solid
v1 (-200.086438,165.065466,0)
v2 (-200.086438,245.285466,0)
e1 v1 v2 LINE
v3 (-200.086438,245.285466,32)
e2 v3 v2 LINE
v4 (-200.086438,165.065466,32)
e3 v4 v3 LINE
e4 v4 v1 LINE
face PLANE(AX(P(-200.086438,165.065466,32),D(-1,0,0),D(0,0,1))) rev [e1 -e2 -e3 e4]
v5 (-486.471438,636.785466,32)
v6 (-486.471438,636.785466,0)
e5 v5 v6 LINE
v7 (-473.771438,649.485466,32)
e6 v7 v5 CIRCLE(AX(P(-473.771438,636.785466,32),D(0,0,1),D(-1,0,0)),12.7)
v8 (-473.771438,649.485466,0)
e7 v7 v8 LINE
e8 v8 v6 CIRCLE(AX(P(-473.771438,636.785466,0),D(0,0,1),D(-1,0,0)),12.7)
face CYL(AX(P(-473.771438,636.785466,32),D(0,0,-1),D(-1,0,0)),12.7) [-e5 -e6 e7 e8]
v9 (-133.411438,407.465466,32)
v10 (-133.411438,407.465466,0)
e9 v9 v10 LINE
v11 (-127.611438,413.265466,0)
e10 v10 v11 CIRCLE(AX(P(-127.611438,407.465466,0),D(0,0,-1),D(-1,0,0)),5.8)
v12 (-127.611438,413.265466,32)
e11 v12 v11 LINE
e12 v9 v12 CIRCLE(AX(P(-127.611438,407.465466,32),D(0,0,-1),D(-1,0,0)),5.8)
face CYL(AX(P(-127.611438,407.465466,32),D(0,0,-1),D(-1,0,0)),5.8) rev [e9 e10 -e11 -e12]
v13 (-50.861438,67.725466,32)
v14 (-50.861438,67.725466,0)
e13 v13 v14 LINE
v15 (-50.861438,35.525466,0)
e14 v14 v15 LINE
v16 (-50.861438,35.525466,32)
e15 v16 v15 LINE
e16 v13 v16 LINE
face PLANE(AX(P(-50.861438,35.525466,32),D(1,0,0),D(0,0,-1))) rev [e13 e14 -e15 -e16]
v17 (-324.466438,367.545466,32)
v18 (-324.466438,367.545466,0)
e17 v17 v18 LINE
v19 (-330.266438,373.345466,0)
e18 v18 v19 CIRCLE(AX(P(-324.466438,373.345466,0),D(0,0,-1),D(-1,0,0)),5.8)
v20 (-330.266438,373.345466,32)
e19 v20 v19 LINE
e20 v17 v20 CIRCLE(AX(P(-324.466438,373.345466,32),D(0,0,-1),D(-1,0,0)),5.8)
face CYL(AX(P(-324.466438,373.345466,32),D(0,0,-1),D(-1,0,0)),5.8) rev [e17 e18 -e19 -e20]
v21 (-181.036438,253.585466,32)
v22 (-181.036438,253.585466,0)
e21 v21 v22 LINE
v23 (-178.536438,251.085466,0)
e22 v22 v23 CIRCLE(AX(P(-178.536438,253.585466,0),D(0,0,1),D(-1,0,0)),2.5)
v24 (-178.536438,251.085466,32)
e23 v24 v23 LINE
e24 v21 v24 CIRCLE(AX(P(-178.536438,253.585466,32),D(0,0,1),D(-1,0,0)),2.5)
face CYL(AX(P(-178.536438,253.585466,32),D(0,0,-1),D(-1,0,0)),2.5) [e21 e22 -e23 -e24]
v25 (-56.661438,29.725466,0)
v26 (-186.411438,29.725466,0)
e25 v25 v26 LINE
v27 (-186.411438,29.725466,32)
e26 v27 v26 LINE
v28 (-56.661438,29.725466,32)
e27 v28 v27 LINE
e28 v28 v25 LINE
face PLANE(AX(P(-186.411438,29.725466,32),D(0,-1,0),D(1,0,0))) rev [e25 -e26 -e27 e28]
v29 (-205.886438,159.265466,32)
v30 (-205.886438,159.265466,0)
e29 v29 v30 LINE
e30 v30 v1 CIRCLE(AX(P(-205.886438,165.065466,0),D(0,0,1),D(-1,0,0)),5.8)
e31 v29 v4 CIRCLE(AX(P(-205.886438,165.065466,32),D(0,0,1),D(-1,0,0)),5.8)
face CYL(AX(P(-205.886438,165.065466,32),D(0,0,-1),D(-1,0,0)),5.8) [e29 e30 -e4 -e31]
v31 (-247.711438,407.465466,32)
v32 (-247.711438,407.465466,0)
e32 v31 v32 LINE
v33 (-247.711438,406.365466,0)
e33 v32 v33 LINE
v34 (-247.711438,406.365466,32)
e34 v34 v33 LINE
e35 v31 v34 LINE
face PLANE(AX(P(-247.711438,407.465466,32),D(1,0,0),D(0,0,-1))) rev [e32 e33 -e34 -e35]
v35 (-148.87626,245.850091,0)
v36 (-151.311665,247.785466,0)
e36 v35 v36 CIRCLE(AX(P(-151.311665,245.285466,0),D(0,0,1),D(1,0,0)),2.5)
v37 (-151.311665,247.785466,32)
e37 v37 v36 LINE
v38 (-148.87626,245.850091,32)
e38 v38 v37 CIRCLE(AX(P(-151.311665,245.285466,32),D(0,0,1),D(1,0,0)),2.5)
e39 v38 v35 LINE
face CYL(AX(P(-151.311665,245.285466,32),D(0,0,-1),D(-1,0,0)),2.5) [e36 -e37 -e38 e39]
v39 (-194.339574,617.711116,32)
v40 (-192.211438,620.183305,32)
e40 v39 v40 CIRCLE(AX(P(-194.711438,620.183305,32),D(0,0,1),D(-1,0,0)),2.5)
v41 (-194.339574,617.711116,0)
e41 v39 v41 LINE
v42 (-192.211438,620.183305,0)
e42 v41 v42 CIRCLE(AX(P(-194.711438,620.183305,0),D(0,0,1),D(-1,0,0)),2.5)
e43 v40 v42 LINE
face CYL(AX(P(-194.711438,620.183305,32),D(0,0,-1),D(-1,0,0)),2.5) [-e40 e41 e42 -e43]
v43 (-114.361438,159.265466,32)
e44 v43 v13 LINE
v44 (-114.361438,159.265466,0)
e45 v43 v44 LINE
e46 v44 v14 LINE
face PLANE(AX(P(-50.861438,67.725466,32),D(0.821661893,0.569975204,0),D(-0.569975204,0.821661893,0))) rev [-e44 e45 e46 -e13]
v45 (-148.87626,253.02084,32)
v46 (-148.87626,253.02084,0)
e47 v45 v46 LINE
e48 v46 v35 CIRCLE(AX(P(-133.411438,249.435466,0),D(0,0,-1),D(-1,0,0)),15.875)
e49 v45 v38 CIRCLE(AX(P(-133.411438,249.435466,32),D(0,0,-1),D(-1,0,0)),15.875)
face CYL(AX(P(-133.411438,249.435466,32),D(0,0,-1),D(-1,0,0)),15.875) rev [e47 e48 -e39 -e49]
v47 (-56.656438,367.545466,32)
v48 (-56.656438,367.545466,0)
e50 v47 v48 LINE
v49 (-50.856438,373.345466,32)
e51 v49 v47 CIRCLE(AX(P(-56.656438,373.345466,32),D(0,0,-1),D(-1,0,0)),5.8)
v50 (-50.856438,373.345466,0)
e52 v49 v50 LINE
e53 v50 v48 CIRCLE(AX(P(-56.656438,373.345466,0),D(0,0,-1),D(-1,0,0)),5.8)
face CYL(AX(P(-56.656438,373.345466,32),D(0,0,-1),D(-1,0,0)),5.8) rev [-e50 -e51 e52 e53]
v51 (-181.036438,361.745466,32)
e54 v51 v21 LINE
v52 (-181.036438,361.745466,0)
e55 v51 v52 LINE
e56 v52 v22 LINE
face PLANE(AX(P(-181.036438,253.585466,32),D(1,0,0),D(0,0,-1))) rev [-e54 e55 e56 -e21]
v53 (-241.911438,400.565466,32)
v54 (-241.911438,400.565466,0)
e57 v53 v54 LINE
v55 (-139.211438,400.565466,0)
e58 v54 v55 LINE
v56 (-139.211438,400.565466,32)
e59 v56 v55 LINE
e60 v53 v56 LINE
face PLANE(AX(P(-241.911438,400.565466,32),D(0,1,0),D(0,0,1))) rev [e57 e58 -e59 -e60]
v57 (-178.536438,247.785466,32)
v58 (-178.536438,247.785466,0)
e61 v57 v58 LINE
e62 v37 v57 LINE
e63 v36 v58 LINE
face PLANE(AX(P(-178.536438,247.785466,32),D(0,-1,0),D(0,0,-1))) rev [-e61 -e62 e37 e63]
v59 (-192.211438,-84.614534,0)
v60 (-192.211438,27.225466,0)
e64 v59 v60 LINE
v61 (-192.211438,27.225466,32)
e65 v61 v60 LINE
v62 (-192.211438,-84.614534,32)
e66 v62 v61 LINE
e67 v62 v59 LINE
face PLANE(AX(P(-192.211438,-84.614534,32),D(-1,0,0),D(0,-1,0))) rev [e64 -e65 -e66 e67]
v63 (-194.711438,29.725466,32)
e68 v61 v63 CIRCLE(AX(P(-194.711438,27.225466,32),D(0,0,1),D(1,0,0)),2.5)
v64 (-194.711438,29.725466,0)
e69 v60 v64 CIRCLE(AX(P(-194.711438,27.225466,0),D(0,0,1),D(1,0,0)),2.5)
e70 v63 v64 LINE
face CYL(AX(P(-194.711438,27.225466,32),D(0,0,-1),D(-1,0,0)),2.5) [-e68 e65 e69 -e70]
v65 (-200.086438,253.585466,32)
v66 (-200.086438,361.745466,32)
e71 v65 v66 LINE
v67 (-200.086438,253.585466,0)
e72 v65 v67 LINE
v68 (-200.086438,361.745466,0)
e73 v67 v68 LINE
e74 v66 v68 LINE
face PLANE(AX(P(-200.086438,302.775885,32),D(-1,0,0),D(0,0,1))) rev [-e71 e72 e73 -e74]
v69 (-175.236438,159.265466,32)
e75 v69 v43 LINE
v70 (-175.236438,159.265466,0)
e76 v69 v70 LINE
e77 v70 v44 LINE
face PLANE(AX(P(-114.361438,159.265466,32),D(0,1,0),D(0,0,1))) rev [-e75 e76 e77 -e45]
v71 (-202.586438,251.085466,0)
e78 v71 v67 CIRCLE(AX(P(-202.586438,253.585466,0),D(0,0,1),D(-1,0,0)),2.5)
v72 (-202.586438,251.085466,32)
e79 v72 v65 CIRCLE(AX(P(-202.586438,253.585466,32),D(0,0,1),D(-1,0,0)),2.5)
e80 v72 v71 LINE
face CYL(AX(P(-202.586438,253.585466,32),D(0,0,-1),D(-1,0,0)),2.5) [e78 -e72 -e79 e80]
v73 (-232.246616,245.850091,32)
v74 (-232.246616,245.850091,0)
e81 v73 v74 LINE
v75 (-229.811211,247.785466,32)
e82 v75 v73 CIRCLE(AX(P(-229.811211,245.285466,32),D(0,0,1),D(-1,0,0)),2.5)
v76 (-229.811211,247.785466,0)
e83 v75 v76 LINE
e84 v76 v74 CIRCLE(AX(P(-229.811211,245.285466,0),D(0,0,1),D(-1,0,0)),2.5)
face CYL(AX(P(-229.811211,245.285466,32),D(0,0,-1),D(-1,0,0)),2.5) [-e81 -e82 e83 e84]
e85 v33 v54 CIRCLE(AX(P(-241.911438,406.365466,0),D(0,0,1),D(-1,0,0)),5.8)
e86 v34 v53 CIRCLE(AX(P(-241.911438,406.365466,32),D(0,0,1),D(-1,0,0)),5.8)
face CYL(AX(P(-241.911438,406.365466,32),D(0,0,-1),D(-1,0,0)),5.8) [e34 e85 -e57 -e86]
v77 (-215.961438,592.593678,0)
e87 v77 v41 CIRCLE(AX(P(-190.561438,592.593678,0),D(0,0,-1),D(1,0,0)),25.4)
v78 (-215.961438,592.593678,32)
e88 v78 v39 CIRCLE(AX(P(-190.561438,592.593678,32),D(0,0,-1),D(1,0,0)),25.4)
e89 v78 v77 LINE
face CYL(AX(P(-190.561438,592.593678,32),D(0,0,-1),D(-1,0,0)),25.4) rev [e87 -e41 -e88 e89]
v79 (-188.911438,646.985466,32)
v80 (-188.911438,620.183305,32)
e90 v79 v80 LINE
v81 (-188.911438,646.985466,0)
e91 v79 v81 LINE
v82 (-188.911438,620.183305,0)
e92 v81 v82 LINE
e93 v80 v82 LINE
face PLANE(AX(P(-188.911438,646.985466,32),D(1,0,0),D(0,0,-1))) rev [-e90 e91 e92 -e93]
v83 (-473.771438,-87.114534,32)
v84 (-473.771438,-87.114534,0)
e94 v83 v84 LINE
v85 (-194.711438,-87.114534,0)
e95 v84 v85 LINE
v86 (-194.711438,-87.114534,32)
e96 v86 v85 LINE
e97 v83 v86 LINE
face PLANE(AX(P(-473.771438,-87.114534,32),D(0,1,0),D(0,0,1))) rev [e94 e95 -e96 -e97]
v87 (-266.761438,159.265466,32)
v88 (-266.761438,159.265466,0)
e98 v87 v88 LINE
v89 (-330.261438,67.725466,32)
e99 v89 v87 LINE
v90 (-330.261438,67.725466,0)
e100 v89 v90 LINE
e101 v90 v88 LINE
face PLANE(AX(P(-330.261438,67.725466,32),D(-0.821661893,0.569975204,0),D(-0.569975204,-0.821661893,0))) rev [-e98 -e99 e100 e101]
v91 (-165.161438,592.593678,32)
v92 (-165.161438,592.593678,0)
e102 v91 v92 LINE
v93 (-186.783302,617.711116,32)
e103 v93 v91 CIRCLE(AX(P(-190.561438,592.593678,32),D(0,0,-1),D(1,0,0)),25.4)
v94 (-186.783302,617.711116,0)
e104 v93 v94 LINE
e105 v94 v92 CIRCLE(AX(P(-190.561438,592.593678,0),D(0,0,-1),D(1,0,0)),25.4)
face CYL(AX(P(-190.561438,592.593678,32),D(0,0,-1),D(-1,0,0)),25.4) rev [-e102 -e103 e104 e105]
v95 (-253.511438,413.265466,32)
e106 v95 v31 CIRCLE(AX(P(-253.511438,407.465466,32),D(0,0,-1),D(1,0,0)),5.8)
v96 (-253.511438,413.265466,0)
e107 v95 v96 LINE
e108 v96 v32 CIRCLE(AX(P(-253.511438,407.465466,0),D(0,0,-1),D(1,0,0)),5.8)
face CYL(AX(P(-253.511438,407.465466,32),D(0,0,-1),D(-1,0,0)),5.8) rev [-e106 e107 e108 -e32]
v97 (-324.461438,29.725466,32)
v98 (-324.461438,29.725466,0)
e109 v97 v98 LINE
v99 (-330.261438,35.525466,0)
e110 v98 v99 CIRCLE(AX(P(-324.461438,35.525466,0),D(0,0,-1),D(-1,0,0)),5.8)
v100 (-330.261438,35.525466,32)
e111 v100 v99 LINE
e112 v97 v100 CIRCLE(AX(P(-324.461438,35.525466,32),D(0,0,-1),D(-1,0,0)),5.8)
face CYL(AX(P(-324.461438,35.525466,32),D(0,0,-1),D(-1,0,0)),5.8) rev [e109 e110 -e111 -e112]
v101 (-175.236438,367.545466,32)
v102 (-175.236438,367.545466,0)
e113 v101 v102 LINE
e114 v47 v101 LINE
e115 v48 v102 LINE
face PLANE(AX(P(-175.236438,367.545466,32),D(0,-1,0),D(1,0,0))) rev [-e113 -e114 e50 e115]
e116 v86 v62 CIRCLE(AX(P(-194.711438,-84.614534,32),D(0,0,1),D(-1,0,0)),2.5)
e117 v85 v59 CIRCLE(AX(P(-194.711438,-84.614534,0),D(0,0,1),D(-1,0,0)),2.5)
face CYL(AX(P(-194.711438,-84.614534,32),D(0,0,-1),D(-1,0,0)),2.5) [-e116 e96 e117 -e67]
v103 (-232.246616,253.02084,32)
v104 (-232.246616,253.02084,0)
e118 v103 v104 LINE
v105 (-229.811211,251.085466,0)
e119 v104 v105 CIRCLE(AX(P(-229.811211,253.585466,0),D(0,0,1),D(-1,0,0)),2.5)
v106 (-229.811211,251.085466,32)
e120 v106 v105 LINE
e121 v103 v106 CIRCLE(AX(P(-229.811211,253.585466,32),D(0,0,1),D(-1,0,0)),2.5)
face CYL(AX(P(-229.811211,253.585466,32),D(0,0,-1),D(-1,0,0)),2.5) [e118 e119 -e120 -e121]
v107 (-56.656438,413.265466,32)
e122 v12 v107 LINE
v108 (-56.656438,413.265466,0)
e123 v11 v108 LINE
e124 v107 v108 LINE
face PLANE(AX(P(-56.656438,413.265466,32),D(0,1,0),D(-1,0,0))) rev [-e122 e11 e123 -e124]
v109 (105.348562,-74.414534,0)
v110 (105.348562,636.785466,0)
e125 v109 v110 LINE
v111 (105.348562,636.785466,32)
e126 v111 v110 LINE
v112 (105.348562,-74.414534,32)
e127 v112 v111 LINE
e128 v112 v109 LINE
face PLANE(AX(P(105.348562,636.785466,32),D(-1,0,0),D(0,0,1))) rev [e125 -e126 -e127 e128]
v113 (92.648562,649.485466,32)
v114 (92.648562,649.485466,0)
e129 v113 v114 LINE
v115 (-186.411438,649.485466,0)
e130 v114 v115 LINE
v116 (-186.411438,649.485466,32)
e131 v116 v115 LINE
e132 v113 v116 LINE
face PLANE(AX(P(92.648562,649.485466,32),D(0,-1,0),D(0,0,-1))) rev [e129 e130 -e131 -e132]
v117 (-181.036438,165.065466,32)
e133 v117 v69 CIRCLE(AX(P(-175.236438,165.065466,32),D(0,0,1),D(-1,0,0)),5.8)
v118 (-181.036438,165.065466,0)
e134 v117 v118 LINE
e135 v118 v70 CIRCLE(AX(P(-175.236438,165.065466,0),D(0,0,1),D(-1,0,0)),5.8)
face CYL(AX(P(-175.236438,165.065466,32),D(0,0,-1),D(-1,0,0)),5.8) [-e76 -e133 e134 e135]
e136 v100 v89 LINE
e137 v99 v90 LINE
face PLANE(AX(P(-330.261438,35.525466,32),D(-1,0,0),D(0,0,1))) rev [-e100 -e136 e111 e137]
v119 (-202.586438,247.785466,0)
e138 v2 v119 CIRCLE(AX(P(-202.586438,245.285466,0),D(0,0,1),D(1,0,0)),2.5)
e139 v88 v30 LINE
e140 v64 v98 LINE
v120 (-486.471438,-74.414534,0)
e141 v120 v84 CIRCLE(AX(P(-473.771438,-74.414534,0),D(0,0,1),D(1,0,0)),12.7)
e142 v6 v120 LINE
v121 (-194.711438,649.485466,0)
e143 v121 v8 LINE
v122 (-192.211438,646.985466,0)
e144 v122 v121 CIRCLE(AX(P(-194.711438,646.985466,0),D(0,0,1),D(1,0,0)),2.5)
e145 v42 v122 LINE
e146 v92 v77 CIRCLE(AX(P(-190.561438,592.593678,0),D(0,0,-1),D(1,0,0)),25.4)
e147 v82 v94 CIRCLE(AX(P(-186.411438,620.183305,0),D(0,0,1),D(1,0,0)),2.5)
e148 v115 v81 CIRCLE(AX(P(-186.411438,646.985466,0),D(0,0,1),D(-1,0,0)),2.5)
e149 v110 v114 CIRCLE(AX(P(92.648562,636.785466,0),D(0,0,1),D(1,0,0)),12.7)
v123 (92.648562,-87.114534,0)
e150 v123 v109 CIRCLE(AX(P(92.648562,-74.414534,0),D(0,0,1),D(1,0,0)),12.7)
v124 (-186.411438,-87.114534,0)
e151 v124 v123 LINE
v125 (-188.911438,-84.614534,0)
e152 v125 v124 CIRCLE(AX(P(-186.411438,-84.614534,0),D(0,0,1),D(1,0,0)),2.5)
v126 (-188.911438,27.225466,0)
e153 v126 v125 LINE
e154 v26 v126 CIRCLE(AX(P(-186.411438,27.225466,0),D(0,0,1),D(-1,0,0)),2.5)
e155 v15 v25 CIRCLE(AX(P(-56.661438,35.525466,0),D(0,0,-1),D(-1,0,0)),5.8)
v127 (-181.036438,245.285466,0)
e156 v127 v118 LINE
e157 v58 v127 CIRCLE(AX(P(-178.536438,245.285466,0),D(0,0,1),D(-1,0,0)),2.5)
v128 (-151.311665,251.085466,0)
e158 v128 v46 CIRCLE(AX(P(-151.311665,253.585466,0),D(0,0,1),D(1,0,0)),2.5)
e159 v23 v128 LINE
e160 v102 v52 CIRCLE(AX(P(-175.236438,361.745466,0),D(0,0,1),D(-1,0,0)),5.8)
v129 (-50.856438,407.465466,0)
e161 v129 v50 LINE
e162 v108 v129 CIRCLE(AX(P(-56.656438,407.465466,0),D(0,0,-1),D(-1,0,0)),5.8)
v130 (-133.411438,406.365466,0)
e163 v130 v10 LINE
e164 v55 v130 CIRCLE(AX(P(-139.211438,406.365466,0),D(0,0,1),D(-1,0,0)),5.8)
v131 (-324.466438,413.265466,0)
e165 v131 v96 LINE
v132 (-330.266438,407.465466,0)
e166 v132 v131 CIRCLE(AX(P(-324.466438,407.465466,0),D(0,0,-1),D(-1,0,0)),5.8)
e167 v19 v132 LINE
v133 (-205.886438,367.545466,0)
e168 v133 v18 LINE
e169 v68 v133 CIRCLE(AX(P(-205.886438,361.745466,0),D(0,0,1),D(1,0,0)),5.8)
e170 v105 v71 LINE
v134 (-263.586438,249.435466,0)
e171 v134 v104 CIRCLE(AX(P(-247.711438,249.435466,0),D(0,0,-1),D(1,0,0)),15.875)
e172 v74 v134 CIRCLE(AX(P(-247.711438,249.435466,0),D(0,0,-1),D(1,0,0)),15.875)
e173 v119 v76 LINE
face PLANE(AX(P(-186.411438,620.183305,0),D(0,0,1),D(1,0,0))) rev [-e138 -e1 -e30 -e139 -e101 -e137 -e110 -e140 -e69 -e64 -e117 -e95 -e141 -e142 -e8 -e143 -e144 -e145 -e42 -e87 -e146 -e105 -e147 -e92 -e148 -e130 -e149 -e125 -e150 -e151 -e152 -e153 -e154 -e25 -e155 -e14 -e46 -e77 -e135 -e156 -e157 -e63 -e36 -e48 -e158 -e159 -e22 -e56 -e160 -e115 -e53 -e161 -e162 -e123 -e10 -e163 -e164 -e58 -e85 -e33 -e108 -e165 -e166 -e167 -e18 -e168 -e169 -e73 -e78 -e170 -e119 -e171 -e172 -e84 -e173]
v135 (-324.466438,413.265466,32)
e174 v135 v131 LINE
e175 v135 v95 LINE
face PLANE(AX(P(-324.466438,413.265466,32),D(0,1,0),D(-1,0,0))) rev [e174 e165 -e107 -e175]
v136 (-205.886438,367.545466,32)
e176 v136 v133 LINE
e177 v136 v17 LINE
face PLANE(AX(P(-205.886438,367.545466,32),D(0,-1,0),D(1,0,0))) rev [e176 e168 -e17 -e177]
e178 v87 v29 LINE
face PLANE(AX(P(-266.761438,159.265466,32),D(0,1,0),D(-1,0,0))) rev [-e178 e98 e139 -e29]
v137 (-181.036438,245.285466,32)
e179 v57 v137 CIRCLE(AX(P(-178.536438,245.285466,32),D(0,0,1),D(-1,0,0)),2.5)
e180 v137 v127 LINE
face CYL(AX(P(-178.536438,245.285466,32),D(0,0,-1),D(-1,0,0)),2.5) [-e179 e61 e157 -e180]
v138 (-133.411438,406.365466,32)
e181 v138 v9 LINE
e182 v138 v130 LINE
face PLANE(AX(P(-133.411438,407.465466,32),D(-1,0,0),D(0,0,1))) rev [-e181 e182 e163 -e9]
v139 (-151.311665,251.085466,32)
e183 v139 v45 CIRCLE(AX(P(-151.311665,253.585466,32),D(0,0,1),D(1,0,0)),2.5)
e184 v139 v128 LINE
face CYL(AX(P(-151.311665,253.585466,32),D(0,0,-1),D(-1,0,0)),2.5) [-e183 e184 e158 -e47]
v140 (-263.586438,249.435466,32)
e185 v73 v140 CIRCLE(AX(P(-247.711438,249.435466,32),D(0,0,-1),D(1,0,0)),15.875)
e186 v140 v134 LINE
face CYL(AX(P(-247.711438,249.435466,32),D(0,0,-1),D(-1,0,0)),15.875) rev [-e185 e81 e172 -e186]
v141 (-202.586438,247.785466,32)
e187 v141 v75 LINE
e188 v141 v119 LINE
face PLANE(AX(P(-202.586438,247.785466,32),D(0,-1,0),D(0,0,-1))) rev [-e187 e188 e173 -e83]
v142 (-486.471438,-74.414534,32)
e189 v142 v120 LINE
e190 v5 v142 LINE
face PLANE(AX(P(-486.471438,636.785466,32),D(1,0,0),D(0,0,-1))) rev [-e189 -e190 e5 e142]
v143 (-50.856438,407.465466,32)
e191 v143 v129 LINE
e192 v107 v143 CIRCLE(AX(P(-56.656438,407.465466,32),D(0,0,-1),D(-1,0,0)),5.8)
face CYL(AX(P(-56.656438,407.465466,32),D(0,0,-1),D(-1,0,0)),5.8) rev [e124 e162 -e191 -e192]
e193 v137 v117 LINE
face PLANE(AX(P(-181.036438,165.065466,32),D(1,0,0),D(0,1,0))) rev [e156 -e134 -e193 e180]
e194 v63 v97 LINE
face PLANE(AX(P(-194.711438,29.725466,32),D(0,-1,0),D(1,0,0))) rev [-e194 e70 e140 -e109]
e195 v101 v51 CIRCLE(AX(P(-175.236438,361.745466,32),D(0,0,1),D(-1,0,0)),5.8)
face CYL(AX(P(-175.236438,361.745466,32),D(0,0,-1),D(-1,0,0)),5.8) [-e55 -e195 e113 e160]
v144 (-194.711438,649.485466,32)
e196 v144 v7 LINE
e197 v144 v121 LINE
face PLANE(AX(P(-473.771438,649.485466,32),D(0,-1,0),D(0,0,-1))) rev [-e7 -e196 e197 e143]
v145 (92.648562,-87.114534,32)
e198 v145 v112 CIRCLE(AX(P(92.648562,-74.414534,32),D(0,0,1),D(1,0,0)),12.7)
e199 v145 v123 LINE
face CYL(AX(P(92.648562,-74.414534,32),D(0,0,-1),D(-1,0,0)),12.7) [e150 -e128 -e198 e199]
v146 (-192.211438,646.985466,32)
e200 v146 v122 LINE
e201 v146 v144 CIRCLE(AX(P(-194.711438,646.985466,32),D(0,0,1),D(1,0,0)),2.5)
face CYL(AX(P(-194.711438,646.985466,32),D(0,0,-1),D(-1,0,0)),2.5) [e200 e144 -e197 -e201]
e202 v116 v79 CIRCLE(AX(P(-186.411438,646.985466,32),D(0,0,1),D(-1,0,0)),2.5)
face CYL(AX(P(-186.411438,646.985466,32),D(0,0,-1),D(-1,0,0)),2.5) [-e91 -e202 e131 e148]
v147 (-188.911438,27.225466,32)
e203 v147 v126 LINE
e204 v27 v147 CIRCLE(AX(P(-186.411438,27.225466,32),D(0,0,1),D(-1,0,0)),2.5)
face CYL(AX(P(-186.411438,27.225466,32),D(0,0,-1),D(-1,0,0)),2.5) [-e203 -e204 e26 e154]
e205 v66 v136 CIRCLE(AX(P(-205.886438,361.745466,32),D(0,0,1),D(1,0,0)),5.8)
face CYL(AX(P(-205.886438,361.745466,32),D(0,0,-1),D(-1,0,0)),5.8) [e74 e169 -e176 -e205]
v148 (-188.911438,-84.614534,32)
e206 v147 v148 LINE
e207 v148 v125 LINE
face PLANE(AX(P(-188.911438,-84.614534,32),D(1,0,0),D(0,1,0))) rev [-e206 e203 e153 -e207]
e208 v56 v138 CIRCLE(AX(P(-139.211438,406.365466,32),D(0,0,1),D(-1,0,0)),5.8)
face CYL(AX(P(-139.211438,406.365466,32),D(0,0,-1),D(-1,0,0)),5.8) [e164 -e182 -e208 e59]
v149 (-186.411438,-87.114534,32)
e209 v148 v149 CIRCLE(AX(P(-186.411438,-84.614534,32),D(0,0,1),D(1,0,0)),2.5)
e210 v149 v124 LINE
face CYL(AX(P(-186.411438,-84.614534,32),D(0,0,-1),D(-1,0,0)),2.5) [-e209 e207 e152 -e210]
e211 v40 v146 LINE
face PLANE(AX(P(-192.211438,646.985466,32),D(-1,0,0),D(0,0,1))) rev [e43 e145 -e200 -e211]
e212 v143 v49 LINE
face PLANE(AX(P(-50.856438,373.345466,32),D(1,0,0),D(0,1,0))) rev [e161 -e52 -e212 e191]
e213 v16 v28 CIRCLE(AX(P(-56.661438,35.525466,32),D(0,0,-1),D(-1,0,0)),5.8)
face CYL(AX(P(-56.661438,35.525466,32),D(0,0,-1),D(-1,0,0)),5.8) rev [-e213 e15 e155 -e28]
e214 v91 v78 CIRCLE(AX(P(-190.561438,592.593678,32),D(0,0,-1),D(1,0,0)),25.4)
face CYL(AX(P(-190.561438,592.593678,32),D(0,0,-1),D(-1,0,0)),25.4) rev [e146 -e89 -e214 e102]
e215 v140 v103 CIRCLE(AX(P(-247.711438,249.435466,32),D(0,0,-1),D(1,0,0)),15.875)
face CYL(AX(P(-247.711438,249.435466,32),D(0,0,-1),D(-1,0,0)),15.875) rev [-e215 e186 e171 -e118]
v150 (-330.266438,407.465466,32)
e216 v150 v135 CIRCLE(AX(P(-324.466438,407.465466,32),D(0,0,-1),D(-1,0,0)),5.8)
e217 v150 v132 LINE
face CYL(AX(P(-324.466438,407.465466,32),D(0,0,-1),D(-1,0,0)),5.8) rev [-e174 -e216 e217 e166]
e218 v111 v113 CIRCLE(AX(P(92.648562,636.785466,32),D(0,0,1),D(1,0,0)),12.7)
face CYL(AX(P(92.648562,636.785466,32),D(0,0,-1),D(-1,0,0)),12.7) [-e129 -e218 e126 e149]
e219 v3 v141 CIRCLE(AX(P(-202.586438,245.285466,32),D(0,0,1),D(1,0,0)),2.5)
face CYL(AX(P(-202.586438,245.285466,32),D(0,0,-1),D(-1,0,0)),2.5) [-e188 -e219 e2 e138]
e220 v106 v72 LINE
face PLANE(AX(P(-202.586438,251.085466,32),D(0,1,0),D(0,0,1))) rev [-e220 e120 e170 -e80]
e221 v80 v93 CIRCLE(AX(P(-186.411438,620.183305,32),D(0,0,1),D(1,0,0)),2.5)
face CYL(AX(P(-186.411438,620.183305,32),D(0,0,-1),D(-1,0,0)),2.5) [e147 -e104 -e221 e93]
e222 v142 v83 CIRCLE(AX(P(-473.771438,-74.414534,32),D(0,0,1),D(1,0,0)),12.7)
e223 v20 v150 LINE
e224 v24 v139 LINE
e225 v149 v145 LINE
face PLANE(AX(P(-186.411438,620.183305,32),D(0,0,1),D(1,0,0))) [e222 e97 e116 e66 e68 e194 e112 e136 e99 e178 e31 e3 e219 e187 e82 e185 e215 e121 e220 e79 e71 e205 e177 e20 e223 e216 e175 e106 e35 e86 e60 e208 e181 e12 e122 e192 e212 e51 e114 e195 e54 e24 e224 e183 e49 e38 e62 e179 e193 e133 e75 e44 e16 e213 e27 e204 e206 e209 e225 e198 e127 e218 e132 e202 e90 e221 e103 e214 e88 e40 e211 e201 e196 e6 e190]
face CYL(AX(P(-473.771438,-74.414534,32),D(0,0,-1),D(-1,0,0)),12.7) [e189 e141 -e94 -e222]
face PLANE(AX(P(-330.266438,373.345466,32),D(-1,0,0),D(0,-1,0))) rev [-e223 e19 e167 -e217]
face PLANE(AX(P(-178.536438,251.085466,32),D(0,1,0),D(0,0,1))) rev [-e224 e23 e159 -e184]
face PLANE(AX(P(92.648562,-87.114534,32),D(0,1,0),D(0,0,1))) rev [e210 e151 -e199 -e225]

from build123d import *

# Parameters (mm, degrees)
BOSS_EXTRUDE1_DEPTH = 32


with BuildPart() as part:
    # Sketch1 → Boss-Extrude1 (new body)
    with BuildSketch(Plane.XY):
        with BuildLine():
            Line((-473.771437729, 649.485465586), (-194.711437729, 649.485465586))
            ThreePointArc((-194.711437729, 649.485465586), (-192.943670776, 648.753232539), (-192.211437729, 646.985465586))
            Line((-192.211437729, 646.985465586), (-192.211437729, 620.183304835))
            ThreePointArc((-192.211437729, 620.183304835), (-192.816753125, 618.552301999), (-194.33957393, 617.711116065))
            ThreePointArc((-194.33957393, 617.711116065), (-190.561437729, 567.193678161), (-186.783301529, 617.711116065))
            ThreePointArc((-186.783301529, 617.711116065), (-188.306122334, 618.552301999), (-188.911437729, 620.183304835))
            Line((-188.911437729, 620.183304835), (-188.911437729, 646.985465586))
            ThreePointArc((-188.911437729, 646.985465586), (-188.179204682, 648.753232539), (-186.411437729, 649.485465586))
            Line((-186.411437729, 649.485465586), (92.648562271, 649.485465586))
            ThreePointArc((92.648562271, 649.485465586), (101.628818392, 645.765721708), (105.348562271, 636.785465586))
            Line((105.348562271, 636.785465586), (105.348562271, -74.414534414))
            ThreePointArc((105.348562271, -74.414534414), (101.628818392, -83.394790535), (92.648562271, -87.114534414))
            Line((92.648562271, -87.114534414), (-186.411437729, -87.114534414))
            ThreePointArc((-186.411437729, -87.114534414), (-188.179204682, -86.382301366), (-188.911437729, -84.614534414))
            Line((-188.911437729, -84.614534414), (-188.911437729, 27.225465586))
            ThreePointArc((-188.911437729, 27.225465586), (-188.179204682, 28.993232539), (-186.411437729, 29.725465586))
            Line((-186.411437729, 29.725465586), (-56.661437729, 29.725465586))
            ThreePointArc((-56.661437729, 29.725465586), (-52.560218399, 31.424246256), (-50.861437729, 35.525465586))
            Line((-50.861437729, 35.525465586), (-50.861437729, 67.725465586))
            Line((-50.861437729, 67.725465586), (-114.361437729, 159.265465586))
            Line((-114.361437729, 159.265465586), (-175.236437729, 159.265465586))
            ThreePointArc((-175.236437729, 159.265465586), (-179.33765706, 160.964246256), (-181.036437729, 165.065465586))
            Line((-181.036437729, 165.065465586), (-181.036437729, 245.285465586))
            ThreePointArc((-181.036437729, 245.285465586), (-180.304204682, 247.053232539), (-178.536437729, 247.785465586))
            Line((-178.536437729, 247.785465586), (-151.311664683, 247.785465586))
            ThreePointArc((-151.311664683, 247.785465586), (-149.75628123, 247.242704027), (-148.876259656, 245.850091437))
            ThreePointArc((-148.876259656, 245.850091437), (-117.536437729, 249.435465586), (-148.876259656, 253.020839736))
            ThreePointArc((-148.876259656, 253.020839736), (-149.75628123, 251.628227146), (-151.311664683, 251.085465586))
            Line((-151.311664683, 251.085465586), (-178.536437729, 251.085465586))
            ThreePointArc((-178.536437729, 251.085465586), (-180.304204682, 251.817698634), (-181.036437729, 253.585465586))
            Line((-181.036437729, 253.585465586), (-181.036437729, 302.775884834))
            Line((-181.036437729, 302.775884834), (-181.036437729, 361.745465586))
            ThreePointArc((-181.036437729, 361.745465586), (-179.33765706, 365.846684917), (-175.236437729, 367.545465586))
            Line((-175.236437729, 367.545465586), (-56.656437729, 367.545465586))
            ThreePointArc((-56.656437729, 367.545465586), (-52.555218399, 369.244246256), (-50.856437729, 373.345465586))
            Line((-50.856437729, 373.345465586), (-50.856437729, 407.465465586))
            ThreePointArc((-50.856437729, 407.465465586), (-52.555218399, 411.566684917), (-56.656437729, 413.265465586))
            Line((-56.656437729, 413.265465586), (-127.611437729, 413.265465586))
            ThreePointArc((-127.611437729, 413.265465586), (-131.71265706, 411.566684917), (-133.411437729, 407.465465586))
            Line((-133.411437729, 407.465465586), (-133.411437729, 406.365465586))
            ThreePointArc((-133.411437729, 406.365465586), (-135.110218399, 402.264246256), (-139.211437729, 400.565465586))
            Line((-139.211437729, 400.565465586), (-241.911437729, 400.565465586))
            ThreePointArc((-241.911437729, 400.565465586), (-246.01265706, 402.264246256), (-247.711437729, 406.365465586))
            Line((-247.711437729, 406.365465586), (-247.711437729, 407.465465586))
            ThreePointArc((-247.711437729, 407.465465586), (-249.410218399, 411.566684917), (-253.511437729, 413.265465586))
            Line((-253.511437729, 413.265465586), (-324.466437729, 413.265465586))
            ThreePointArc((-324.466437729, 413.265465586), (-328.56765706, 411.566684917), (-330.266437729, 407.465465586))
            Line((-330.266437729, 407.465465586), (-330.266437729, 373.345465586))
            ThreePointArc((-330.266437729, 373.345465586), (-328.56765706, 369.244246256), (-324.466437729, 367.545465586))
            Line((-324.466437729, 367.545465586), (-205.886437729, 367.545465586))
            ThreePointArc((-205.886437729, 367.545465586), (-201.785218399, 365.846684917), (-200.086437729, 361.745465586))
            Line((-200.086437729, 361.745465586), (-200.086437729, 302.775884834))
            Line((-200.086437729, 302.775884834), (-200.086437729, 253.585465586))
            ThreePointArc((-200.086437729, 253.585465586), (-200.818670776, 251.817698634), (-202.586437729, 251.085465586))
            Line((-202.586437729, 251.085465586), (-229.811210776, 251.085465586))
            ThreePointArc((-229.811210776, 251.085465586), (-231.366594229, 251.628227146), (-232.246615803, 253.020839736))
            ThreePointArc((-232.246615803, 253.020839736), (-263.586437729, 249.435465586), (-232.246615803, 245.850091437))
            ThreePointArc((-232.246615803, 245.850091437), (-231.366594229, 247.242704027), (-229.811210776, 247.785465586))
            Line((-229.811210776, 247.785465586), (-202.586437729, 247.785465586))
            ThreePointArc((-202.586437729, 247.785465586), (-200.818670776, 247.053232539), (-200.086437729, 245.285465586))
            Line((-200.086437729, 245.285465586), (-200.086437729, 165.065465586))
            ThreePointArc((-200.086437729, 165.065465586), (-201.785218399, 160.964246256), (-205.886437729, 159.265465586))
            Line((-205.886437729, 159.265465586), (-266.761437729, 159.265465586))
            Line((-266.761437729, 159.265465586), (-330.261437729, 67.725465586))
            Line((-330.261437729, 67.725465586), (-330.261437729, 35.525465586))
            ThreePointArc((-330.261437729, 35.525465586), (-328.56265706, 31.424246256), (-324.461437729, 29.725465586))
            Line((-324.461437729, 29.725465586), (-194.711437729, 29.725465586))
            ThreePointArc((-194.711437729, 29.725465586), (-192.943670776, 28.993232539), (-192.211437729, 27.225465586))
            Line((-192.211437729, 27.225465586), (-192.211437729, -84.614534414))
            ThreePointArc((-192.211437729, -84.614534414), (-192.943670776, -86.382301366), (-194.711437729, -87.114534414))
            Line((-194.711437729, -87.114534414), (-473.771437729, -87.114534414))
            ThreePointArc((-473.771437729, -87.114534414), (-482.751693851, -83.394790535), (-486.471437729, -74.414534414))
            Line((-486.471437729, -74.414534414), (-486.471437729, 636.785465586))
            ThreePointArc((-486.471437729, 636.785465586), (-482.751693851, 645.765721708), (-473.771437729, 649.485465586))
        make_face()
    extrude(amount=BOSS_EXTRUDE1_DEPTH)


solid = part.part
